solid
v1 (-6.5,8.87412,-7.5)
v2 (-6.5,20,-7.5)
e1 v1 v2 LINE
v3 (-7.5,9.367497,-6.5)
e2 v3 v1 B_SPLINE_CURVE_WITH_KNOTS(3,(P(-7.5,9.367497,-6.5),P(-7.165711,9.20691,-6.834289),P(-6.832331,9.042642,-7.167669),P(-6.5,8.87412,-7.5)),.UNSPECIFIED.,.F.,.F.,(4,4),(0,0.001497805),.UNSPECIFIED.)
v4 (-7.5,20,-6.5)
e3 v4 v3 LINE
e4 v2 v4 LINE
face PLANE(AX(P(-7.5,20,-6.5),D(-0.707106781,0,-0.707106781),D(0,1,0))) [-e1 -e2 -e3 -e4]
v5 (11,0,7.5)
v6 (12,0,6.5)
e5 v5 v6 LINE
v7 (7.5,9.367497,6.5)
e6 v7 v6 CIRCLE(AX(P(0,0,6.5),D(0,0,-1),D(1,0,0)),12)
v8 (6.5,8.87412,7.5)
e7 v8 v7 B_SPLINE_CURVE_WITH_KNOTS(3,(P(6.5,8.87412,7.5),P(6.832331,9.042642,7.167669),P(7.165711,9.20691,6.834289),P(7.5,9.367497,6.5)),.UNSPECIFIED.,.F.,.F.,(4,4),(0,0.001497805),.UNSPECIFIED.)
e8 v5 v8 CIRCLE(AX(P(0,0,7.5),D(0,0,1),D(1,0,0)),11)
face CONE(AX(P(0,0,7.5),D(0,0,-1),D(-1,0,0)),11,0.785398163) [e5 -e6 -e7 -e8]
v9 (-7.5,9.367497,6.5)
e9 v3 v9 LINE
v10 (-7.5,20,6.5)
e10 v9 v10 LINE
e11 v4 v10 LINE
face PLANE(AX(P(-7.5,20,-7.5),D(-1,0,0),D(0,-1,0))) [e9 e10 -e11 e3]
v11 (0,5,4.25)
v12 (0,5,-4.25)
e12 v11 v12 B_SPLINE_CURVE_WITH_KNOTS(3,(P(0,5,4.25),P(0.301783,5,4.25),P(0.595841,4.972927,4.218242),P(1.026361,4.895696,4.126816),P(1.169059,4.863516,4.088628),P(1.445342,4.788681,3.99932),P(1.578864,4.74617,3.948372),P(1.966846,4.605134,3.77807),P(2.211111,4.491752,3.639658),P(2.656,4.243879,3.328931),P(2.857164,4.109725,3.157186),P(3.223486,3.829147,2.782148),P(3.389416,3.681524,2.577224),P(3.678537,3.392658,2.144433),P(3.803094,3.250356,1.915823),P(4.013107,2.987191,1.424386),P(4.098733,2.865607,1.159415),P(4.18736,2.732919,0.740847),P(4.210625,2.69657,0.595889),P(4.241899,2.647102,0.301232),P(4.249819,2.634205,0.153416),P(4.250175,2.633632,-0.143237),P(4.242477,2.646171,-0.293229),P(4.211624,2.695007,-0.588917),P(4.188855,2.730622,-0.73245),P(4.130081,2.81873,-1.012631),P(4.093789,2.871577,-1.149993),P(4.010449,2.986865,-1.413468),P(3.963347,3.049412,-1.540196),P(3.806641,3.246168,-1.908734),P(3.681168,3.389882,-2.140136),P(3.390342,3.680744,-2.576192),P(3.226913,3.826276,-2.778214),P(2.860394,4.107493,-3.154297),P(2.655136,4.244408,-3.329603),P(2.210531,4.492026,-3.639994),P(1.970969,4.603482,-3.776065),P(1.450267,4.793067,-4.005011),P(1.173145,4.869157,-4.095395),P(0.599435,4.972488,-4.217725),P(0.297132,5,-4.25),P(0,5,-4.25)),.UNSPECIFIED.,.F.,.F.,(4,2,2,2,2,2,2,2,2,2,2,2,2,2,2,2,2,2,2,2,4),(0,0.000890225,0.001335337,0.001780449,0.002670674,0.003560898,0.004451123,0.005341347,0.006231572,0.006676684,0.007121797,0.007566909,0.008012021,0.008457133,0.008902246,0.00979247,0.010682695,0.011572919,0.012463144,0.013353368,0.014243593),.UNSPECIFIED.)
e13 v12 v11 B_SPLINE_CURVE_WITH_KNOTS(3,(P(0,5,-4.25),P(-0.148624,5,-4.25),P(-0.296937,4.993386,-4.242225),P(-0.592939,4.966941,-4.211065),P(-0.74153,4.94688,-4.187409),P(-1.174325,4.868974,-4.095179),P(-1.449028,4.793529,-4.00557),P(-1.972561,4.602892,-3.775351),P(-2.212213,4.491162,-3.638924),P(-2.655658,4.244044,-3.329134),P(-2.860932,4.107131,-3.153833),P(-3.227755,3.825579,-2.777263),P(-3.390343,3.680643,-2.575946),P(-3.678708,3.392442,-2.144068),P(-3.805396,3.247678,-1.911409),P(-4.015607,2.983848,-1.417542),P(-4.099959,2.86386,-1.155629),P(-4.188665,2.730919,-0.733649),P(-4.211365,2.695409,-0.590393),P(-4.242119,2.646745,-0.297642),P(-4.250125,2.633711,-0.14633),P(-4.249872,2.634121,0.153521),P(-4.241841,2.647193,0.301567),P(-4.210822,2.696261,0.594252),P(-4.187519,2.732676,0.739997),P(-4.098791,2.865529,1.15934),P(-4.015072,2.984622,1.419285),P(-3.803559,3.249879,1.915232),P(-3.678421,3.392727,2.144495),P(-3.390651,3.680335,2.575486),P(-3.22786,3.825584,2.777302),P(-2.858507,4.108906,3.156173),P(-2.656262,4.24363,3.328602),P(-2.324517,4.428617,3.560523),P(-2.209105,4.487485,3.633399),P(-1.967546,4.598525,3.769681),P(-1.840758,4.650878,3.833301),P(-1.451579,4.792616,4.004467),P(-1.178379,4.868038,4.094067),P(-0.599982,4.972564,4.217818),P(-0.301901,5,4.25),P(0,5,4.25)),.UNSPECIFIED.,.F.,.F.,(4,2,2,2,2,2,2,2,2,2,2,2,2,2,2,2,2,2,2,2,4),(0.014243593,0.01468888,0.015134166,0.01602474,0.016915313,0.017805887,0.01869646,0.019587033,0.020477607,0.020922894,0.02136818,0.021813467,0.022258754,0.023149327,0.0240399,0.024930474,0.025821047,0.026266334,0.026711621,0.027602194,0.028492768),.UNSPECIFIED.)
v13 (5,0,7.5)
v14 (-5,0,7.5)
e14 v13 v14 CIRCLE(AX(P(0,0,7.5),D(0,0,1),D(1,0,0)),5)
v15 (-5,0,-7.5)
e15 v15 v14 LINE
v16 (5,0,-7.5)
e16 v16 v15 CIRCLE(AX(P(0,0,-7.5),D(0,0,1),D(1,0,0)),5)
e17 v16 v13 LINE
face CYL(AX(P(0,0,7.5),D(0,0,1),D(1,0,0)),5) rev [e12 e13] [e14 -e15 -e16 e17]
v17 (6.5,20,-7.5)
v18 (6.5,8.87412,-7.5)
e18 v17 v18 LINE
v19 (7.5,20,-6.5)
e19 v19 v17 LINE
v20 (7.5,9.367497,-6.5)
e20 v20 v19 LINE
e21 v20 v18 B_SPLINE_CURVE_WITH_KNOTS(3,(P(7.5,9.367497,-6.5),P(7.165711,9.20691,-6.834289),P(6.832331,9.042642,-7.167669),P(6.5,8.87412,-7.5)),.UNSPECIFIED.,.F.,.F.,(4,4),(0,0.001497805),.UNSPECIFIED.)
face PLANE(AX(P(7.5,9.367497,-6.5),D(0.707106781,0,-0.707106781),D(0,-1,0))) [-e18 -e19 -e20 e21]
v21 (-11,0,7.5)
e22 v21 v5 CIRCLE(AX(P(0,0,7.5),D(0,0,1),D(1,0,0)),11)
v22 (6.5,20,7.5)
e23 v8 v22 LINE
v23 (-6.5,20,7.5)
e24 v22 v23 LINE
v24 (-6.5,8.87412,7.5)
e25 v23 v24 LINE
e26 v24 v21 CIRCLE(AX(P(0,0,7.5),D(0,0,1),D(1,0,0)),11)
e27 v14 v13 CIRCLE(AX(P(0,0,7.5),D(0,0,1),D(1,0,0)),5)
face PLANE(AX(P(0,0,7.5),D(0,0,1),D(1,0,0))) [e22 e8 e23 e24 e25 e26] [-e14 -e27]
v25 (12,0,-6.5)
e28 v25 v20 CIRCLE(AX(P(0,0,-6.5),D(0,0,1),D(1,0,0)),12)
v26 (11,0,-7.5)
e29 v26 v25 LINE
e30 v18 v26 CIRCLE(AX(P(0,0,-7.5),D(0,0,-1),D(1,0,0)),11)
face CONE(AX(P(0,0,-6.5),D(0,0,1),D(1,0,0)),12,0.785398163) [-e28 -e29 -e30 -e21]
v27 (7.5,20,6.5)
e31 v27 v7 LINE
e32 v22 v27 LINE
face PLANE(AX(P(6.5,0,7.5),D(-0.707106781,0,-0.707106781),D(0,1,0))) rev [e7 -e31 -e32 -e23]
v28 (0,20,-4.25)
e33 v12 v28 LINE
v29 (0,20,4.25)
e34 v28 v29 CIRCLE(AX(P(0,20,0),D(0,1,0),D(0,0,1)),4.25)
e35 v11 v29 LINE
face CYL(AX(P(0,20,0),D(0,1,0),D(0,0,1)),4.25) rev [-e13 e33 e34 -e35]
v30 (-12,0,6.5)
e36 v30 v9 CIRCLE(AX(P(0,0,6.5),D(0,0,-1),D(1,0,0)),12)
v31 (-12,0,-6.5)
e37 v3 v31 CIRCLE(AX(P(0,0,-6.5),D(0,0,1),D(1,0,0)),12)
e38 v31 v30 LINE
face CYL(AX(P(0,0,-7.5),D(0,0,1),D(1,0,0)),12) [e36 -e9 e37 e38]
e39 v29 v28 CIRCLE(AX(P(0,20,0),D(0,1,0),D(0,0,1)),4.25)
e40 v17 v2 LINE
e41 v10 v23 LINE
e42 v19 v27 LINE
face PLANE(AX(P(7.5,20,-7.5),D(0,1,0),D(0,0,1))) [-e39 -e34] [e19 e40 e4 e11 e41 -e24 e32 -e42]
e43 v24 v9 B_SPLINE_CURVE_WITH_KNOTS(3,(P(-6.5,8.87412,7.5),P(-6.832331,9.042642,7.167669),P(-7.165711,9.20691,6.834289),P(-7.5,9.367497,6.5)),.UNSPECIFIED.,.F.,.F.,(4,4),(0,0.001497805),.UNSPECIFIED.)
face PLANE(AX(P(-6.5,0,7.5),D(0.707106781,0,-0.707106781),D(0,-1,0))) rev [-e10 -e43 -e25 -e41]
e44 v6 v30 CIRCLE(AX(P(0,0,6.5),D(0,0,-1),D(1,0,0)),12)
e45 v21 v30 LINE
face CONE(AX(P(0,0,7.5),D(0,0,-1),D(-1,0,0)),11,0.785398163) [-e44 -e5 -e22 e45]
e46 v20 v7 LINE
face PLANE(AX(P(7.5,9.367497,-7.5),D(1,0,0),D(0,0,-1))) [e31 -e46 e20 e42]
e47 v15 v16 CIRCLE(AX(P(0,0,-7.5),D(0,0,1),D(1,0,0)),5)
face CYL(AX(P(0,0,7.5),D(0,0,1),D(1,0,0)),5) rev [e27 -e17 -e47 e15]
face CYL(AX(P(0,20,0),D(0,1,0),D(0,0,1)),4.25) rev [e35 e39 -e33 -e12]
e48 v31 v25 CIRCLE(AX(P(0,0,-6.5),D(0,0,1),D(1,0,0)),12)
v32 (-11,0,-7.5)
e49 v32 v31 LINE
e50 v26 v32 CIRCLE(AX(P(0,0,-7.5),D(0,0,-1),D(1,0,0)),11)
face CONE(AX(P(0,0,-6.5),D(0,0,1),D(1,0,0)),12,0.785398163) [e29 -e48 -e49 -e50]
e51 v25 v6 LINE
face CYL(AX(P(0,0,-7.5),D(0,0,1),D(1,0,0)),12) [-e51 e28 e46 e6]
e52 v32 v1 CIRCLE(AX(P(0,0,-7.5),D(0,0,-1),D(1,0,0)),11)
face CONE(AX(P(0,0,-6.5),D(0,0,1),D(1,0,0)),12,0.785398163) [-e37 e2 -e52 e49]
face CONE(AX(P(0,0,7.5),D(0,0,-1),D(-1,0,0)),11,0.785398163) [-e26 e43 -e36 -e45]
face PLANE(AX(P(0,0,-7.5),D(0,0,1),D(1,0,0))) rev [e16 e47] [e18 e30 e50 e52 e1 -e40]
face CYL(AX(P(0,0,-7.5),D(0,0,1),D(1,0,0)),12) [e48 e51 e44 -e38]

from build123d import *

# Parameters (mm, degrees)
EXTRUDE_1_DEPTH              = 15
HOLE_WIZARD_10_0_10_1_D      = 10
HOLE_WIZARD_8_5_8_5_1_REACH  = 36.989
HOLE_WIZARD_8_5_8_5_1_BORE_R = 4.25
CHAMFER_1_SIZE               = 1


with BuildPart() as part:
    # 草图1 → 凸台-拉伸1 (new body)
    with BuildSketch(Plane.XY.offset(7.5)):
        with BuildLine():
            Line((7.5, 20), (-7.5, 20))
            Line((-7.5, 20), (-7.5, 9.367496998))
            ThreePointArc((-7.5, 9.367496998), (0, -12), (7.5, 9.367496998))
            Line((7.5, 9.367496998), (7.5, 20))
        make_face()
    extrude(amount=-EXTRUDE_1_DEPTH)

    # Ø10.0 (10) 直径孔1 (through all)
    with Locations(Plane.XY.offset(7.5)):
        with Locations((0, 0)):
            Hole(HOLE_WIZARD_10_0_10_1_D / 2)

    # Ø8.5 (8.5) 直径孔1 bore → Ø8.5 (8.5) 直径孔1 (cut, up to next)
    with BuildSketch(Plane(origin=(0, 20, 0), x_dir=(1, 0, 0), z_dir=(0, 1, 0)), mode=Mode.PRIVATE) as hole_wizard_8_5_8_5_1_sk1:
        Circle(HOLE_WIZARD_8_5_8_5_1_BORE_R)
    hole_wizard_8_5_8_5_1_tool1 = extrude(hole_wizard_8_5_8_5_1_sk1.sketch, amount=-HOLE_WIZARD_8_5_8_5_1_REACH, mode=Mode.PRIVATE) & part.part
    add(hole_wizard_8_5_8_5_1_tool1.solids().sort_by_distance((0, 20, 0))[0], mode=Mode.SUBTRACT)

    # 倒角1
    chamfer_1_edges = [part.edges().sort_by_distance(p)[0] for p in [
        (-7.5, 14.683748499, -7.5),
        (0, -12, -7.5),
        (7.5, 14.683748499, -7.5),
        (0, -12, 7.5),
        (-7.5, 14.683748499, 7.5),
        (7.5, 14.683748499, 7.5),
    ]]
    chamfer(chamfer_1_edges, length=CHAMFER_1_SIZE)


solid = part.part
